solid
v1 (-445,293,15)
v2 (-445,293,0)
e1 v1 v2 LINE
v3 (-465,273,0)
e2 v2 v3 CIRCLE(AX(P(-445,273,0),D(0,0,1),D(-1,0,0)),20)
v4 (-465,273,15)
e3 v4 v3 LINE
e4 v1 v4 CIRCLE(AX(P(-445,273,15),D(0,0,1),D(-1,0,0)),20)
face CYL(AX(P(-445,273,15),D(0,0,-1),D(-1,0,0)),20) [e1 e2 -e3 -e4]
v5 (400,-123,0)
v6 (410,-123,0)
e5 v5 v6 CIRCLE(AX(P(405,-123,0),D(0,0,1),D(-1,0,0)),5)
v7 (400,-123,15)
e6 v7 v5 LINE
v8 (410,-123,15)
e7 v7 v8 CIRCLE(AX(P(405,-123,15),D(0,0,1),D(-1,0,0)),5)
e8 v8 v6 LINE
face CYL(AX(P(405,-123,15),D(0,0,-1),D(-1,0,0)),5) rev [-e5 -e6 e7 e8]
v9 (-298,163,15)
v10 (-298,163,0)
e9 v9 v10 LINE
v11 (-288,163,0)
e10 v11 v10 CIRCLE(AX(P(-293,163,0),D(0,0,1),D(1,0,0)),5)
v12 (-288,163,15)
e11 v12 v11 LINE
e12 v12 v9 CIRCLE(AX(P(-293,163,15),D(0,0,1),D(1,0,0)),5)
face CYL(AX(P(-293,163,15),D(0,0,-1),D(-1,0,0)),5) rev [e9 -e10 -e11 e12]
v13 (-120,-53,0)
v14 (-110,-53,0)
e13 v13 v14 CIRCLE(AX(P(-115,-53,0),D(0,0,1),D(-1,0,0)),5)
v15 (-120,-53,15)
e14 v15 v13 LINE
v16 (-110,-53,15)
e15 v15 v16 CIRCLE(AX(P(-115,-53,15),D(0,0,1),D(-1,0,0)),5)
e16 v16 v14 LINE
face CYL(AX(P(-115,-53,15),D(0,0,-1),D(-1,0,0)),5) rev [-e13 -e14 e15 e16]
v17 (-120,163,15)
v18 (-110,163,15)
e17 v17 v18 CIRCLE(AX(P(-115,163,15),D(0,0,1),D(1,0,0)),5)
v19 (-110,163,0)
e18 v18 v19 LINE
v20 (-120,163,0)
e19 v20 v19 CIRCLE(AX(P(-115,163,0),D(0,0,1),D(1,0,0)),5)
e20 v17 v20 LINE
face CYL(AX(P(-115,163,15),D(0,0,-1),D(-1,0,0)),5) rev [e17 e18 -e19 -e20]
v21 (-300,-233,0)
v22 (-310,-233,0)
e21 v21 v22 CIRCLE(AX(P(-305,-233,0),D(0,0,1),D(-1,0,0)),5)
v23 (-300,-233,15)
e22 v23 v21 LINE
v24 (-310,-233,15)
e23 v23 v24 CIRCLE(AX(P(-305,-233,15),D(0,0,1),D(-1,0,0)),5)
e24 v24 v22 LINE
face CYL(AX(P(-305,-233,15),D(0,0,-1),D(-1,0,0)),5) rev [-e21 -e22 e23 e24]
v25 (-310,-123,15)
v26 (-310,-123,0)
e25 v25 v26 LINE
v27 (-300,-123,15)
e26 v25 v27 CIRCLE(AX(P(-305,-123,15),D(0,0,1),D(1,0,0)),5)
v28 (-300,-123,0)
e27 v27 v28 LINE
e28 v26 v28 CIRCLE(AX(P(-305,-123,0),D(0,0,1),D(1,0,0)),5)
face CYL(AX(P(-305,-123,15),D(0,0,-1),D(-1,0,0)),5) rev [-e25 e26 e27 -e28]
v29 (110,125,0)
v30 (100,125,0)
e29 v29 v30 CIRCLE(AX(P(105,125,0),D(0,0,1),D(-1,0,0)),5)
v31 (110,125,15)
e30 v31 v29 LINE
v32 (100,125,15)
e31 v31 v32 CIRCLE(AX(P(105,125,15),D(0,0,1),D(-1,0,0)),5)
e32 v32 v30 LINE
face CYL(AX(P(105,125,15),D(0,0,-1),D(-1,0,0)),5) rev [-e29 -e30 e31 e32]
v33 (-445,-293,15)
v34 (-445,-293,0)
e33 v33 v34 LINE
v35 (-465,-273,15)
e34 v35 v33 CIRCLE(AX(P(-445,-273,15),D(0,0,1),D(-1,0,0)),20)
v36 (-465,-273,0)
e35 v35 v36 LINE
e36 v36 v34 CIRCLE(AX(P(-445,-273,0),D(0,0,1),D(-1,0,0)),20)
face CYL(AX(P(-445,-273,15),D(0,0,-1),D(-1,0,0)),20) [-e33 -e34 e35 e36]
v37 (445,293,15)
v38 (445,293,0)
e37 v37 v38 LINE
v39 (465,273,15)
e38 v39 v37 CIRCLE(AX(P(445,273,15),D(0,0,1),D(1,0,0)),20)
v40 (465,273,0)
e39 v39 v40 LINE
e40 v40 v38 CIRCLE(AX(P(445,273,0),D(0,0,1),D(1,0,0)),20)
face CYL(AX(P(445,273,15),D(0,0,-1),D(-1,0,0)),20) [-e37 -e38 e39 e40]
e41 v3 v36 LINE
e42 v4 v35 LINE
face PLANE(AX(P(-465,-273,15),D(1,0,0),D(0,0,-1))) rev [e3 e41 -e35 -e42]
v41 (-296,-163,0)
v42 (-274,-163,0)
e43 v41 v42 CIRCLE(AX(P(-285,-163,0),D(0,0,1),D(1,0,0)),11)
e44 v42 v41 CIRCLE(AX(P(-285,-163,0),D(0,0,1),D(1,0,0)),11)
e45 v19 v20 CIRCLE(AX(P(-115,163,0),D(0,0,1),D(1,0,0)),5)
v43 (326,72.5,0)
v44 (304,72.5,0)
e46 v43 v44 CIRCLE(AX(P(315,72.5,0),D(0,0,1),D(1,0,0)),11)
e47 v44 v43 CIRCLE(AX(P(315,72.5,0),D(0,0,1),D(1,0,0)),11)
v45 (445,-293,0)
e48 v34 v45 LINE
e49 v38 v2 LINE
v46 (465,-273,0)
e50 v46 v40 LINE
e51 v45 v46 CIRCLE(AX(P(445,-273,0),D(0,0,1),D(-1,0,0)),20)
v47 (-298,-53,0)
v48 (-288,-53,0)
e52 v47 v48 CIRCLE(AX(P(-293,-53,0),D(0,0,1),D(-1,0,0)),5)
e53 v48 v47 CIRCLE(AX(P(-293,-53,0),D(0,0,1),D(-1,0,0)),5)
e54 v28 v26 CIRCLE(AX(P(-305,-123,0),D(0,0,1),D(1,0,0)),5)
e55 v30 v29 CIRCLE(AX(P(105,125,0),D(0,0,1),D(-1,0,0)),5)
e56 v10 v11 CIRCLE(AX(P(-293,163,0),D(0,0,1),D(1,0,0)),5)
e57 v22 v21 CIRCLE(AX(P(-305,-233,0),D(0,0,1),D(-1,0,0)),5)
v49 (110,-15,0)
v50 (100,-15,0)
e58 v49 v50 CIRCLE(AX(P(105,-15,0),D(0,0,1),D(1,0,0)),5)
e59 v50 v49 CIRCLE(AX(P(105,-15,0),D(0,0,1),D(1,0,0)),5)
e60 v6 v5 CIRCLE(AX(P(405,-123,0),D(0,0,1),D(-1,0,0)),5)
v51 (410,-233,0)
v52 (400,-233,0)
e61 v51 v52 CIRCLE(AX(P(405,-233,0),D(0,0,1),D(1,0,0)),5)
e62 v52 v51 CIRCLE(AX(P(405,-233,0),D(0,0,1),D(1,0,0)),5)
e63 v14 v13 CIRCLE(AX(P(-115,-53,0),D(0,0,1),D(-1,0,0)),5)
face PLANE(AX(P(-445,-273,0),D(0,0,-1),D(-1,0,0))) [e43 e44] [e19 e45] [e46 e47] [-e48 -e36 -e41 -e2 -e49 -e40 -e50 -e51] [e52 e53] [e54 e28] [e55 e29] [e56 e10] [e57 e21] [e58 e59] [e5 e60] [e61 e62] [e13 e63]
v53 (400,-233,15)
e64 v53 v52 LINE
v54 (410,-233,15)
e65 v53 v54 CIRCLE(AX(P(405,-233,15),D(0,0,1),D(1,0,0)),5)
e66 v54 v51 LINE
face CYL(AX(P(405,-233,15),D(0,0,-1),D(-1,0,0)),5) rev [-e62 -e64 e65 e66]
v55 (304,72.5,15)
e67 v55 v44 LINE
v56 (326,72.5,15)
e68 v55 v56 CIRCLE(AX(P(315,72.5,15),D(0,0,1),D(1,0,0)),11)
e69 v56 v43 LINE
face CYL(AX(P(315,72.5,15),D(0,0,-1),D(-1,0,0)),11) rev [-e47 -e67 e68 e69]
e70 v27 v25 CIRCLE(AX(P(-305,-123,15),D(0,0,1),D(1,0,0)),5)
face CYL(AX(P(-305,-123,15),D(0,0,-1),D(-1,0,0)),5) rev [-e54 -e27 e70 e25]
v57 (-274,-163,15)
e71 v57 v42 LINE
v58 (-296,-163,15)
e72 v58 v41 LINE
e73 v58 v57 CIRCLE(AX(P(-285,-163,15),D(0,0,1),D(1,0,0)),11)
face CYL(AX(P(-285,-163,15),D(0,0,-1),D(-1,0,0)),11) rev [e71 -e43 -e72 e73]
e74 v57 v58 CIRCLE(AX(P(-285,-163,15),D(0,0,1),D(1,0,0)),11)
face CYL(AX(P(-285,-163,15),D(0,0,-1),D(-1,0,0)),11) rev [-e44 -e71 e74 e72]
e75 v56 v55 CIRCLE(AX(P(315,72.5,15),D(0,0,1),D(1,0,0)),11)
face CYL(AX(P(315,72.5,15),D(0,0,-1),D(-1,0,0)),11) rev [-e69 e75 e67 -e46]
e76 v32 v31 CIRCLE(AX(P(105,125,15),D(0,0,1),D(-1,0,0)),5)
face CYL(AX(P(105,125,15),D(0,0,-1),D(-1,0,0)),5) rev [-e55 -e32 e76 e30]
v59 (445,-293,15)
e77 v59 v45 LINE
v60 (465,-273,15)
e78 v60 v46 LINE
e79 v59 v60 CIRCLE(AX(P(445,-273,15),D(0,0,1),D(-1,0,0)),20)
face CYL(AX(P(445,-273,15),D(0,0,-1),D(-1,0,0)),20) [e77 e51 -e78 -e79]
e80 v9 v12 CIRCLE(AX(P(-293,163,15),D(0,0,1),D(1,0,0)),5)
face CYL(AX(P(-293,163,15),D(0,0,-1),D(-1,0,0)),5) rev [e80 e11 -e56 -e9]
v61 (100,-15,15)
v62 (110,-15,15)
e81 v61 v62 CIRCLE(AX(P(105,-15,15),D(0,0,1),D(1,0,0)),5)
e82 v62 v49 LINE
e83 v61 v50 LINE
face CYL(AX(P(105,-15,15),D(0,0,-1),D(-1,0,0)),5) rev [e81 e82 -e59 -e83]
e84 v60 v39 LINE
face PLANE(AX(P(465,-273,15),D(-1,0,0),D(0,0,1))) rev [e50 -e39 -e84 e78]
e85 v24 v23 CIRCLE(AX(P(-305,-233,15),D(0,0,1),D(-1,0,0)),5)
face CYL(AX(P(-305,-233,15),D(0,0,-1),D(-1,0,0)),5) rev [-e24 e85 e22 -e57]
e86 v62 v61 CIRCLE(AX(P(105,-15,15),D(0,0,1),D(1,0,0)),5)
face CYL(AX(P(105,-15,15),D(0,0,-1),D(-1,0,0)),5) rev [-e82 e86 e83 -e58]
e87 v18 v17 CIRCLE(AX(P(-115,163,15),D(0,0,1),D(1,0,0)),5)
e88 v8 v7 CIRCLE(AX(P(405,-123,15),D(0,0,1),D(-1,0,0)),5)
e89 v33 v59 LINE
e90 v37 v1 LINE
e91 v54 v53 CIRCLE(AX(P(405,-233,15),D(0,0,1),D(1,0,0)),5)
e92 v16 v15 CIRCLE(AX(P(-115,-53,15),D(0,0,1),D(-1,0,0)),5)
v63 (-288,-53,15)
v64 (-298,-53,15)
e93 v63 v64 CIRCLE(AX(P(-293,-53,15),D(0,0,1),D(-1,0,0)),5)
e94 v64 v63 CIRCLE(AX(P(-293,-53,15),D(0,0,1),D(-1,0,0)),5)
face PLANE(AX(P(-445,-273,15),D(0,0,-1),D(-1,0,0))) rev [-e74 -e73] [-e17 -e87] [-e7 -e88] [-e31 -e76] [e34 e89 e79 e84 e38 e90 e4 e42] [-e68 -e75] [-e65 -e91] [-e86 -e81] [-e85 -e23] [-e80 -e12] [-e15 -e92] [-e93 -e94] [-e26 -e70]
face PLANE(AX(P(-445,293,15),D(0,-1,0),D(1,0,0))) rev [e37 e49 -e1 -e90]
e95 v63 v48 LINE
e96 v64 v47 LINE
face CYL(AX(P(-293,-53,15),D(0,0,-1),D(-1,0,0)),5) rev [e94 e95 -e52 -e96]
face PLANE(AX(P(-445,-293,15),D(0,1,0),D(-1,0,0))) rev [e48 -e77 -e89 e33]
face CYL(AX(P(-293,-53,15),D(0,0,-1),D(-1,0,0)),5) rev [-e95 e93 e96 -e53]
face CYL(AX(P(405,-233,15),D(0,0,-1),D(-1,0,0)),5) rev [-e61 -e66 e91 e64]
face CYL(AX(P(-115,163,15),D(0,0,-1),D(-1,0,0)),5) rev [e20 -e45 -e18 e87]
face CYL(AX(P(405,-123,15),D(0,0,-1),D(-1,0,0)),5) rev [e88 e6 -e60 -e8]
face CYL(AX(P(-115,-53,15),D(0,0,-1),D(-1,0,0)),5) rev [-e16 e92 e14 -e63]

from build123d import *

# Parameters (mm, degrees)
SKETCH_1_R           = 5
SKETCH_1_R_2         = 11
BOSS_EXTRUDE_1_DEPTH = 15


with BuildPart() as part:
    # Sketch 1 → Boss-Extrude 1 (new body)
    with BuildSketch(Plane.XY):
        with BuildLine():
            Line((-465, -273), (-465, 273))
            ThreePointArc((-465, 273), (-459.142135624, 287.142135624), (-445, 293))
            Line((-445, 293), (445, 293))
            ThreePointArc((445, 293), (459.142135624, 287.142135624), (465, 273))
            Line((465, 273), (465, -273))
            ThreePointArc((465, -273), (459.142135624, -287.142135624), (445, -293))
            Line((445, -293), (-445, -293))
            ThreePointArc((-445, -293), (-459.142135624, -287.142135624), (-465, -273))
        make_face()
        with Locations((-115, 163)):
            Circle(SKETCH_1_R, mode=Mode.SUBTRACT)
        with Locations((-293, 163)):
            Circle(SKETCH_1_R, mode=Mode.SUBTRACT)
        with Locations(Location((-293, -53, 0), (0, 0, 180))):
            Circle(SKETCH_1_R, mode=Mode.SUBTRACT)
        with Locations((105, -15)):
            Circle(SKETCH_1_R, mode=Mode.SUBTRACT)
        with Locations(Location((-115, -53, 0), (0, 0, 180))):
            Circle(SKETCH_1_R, mode=Mode.SUBTRACT)
        with Locations(Location((105, 125, 0), (0, 0, 180))):
            Circle(SKETCH_1_R, mode=Mode.SUBTRACT)
        with Locations((-305, -123)):
            Circle(SKETCH_1_R, mode=Mode.SUBTRACT)
        with Locations(Location((-305, -233, 0), (0, 0, 180))):
            Circle(SKETCH_1_R, mode=Mode.SUBTRACT)
        with Locations((405, -233)):
            Circle(SKETCH_1_R, mode=Mode.SUBTRACT)
        with Locations(Location((405, -123, 0), (0, 0, 180))):
            Circle(SKETCH_1_R, mode=Mode.SUBTRACT)
        with Locations((315, 72.5)):
            Circle(SKETCH_1_R_2, mode=Mode.SUBTRACT)
        with Locations((-285, -163)):
            Circle(SKETCH_1_R_2, mode=Mode.SUBTRACT)
    extrude(amount=BOSS_EXTRUDE_1_DEPTH)


solid = part.part
